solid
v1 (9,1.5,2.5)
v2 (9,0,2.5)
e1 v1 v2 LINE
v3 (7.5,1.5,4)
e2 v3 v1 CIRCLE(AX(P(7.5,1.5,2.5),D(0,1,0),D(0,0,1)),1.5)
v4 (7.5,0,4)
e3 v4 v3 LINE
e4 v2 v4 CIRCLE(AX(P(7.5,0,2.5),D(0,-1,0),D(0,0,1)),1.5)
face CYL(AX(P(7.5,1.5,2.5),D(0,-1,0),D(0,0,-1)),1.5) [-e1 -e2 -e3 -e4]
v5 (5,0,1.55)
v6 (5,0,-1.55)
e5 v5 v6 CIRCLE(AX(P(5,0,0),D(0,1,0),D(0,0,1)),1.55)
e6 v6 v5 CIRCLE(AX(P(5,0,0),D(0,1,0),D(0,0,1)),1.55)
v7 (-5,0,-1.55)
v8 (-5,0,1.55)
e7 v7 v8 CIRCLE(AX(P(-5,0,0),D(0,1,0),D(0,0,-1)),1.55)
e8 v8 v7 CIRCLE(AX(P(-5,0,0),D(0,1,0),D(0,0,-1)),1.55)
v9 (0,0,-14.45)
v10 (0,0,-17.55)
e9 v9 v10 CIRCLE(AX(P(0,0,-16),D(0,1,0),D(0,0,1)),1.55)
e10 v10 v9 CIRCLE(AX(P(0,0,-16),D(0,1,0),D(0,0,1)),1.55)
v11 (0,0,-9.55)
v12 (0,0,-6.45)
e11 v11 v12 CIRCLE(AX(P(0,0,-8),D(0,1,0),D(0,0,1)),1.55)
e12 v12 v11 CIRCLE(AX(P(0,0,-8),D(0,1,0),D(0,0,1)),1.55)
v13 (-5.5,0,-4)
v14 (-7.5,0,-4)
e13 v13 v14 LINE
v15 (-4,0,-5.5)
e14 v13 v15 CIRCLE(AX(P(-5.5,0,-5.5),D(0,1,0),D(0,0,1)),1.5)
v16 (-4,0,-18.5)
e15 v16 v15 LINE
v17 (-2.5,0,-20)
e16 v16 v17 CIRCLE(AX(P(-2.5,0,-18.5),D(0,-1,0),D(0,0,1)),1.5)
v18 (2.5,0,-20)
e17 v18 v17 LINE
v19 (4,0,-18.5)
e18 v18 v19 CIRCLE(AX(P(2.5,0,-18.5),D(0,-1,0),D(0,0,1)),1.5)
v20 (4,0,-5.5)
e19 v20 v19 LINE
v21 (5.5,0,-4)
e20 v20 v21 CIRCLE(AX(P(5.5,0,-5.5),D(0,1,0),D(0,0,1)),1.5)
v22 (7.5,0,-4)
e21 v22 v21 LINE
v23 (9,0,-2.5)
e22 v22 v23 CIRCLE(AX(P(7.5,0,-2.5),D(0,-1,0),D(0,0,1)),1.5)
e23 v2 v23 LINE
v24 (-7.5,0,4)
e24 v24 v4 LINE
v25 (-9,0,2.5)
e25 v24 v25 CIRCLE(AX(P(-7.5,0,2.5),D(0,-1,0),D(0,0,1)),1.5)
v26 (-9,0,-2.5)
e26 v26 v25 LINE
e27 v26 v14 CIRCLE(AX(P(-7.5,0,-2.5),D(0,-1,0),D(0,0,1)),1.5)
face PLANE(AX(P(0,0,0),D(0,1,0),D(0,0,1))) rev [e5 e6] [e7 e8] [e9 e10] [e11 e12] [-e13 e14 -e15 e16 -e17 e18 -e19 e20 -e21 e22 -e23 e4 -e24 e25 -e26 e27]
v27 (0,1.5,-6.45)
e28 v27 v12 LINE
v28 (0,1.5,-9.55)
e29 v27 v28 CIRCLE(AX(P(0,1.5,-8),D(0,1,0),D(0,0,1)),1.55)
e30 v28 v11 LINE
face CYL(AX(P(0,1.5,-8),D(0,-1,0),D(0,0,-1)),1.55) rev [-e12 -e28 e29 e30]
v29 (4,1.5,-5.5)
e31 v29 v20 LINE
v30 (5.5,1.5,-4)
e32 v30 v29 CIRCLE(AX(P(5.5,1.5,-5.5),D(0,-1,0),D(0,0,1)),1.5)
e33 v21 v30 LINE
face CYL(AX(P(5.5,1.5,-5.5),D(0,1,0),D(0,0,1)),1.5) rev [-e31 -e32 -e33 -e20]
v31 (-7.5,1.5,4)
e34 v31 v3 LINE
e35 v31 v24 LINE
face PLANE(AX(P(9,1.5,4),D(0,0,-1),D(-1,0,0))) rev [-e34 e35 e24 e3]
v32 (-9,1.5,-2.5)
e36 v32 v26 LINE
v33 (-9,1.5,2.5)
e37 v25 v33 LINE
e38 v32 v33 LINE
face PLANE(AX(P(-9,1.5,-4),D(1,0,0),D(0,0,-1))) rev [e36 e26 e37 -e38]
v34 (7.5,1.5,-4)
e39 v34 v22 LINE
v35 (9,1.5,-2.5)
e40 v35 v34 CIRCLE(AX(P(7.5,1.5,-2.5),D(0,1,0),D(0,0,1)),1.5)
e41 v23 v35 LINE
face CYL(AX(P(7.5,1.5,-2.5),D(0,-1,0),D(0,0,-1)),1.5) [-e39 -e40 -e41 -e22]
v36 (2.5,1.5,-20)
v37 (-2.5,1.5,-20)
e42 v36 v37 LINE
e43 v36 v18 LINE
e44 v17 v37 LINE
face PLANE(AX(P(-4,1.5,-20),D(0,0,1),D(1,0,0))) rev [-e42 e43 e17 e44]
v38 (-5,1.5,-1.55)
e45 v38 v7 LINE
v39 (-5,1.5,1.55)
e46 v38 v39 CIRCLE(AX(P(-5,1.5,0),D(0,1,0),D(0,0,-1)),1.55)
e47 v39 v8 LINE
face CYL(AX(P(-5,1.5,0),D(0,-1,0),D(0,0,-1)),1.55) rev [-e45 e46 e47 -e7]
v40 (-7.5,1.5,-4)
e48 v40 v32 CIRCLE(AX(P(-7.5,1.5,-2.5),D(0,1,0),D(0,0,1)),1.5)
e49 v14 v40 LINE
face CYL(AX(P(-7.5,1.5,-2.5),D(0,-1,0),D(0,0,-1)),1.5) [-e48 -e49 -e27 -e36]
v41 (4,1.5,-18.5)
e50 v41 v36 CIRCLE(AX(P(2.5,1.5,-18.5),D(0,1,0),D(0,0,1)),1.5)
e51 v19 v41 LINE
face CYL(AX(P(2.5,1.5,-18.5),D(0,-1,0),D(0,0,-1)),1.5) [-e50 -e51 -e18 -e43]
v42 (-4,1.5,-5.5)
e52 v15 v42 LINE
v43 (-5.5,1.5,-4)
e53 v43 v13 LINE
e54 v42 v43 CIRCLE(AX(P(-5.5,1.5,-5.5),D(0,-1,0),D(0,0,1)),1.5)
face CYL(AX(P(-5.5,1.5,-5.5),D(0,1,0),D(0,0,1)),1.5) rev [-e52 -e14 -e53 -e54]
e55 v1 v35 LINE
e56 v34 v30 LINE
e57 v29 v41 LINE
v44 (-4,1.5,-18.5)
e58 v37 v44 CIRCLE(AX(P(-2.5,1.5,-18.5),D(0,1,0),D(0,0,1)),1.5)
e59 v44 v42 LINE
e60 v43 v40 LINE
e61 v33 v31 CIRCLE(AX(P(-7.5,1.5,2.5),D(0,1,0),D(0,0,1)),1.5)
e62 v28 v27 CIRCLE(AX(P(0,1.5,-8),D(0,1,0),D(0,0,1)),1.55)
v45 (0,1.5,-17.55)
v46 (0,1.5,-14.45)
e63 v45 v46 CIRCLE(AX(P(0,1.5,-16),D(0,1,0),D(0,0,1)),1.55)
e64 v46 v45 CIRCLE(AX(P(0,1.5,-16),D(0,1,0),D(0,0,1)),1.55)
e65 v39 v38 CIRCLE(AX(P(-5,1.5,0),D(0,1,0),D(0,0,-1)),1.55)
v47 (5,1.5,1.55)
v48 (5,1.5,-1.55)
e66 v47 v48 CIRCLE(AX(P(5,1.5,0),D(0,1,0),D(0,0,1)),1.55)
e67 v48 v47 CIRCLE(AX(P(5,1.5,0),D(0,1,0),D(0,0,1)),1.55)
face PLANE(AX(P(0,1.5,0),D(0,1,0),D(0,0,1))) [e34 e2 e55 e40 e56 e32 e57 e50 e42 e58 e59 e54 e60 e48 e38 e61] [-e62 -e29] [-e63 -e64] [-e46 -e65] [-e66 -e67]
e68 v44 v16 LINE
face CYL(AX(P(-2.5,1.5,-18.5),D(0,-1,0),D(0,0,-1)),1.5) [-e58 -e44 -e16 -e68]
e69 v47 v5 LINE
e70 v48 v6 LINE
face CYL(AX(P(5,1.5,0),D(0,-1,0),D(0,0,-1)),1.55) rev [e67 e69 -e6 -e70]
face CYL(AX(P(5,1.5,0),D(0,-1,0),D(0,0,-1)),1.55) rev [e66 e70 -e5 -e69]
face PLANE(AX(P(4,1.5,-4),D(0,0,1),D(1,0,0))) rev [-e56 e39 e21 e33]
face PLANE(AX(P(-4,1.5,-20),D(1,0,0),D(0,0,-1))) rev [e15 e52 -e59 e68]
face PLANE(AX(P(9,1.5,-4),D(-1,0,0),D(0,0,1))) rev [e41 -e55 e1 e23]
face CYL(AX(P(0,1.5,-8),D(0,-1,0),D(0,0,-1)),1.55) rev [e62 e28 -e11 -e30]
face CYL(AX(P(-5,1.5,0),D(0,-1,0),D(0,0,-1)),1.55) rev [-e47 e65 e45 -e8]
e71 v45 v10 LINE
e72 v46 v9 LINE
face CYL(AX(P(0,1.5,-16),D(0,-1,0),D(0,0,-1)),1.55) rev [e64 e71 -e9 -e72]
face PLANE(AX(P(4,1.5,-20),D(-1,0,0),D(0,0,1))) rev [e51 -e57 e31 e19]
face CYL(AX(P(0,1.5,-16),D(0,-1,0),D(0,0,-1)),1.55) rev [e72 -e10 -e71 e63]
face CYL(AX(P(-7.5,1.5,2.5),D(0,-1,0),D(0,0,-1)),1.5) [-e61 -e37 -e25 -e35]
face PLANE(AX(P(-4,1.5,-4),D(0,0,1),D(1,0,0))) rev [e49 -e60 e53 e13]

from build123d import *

# Parameters (mm, degrees)
SKETCH_1_R      = 1.55
EXTRUDE_1_DEPTH = 1.5
FILLET_1_R      = 1.5


with BuildPart() as part:
    # 草图1 → 凸台-拉伸1 (new body)
    with BuildSketch(Plane(origin=(0, 0, 0), x_dir=(1, 0, 0), z_dir=(0, 1, 0))):
        Polygon((-4, 20), (4, 20), (4, 4), (9, 4), (9, -4), (-9, -4), (-9, 4), (-4, 4), align=None)
        with Locations(Location((5, 0, 0), (0, 0, 270))):
            Circle(SKETCH_1_R, mode=Mode.SUBTRACT)
        with Locations(Location((0, 8, 0), (0, 0, 270))):
            Circle(SKETCH_1_R, mode=Mode.SUBTRACT)
        with Locations(Location((0, 16, 0), (0, 0, 270))):
            Circle(SKETCH_1_R, mode=Mode.SUBTRACT)
        with Locations(Location((-5, 0, 0), (0, 0, 90))):
            Circle(SKETCH_1_R, mode=Mode.SUBTRACT)
    extrude(amount=EXTRUDE_1_DEPTH)

    # 圆角1
    fillet_1_edges = [part.edges().sort_by_distance(p)[0] for p in [
        (4, 0.75, -4),
        (9, 0.75, -4),
        (9, 0.75, 4),
        (-9, 0.75, 4),
        (-9, 0.75, -4),
        (-4, 0.75, -4),
        (-4, 0.75, -20),
        (4, 0.75, -20),
    ]]
    fillet(fillet_1_edges, radius=FILLET_1_R)


solid = part.part
